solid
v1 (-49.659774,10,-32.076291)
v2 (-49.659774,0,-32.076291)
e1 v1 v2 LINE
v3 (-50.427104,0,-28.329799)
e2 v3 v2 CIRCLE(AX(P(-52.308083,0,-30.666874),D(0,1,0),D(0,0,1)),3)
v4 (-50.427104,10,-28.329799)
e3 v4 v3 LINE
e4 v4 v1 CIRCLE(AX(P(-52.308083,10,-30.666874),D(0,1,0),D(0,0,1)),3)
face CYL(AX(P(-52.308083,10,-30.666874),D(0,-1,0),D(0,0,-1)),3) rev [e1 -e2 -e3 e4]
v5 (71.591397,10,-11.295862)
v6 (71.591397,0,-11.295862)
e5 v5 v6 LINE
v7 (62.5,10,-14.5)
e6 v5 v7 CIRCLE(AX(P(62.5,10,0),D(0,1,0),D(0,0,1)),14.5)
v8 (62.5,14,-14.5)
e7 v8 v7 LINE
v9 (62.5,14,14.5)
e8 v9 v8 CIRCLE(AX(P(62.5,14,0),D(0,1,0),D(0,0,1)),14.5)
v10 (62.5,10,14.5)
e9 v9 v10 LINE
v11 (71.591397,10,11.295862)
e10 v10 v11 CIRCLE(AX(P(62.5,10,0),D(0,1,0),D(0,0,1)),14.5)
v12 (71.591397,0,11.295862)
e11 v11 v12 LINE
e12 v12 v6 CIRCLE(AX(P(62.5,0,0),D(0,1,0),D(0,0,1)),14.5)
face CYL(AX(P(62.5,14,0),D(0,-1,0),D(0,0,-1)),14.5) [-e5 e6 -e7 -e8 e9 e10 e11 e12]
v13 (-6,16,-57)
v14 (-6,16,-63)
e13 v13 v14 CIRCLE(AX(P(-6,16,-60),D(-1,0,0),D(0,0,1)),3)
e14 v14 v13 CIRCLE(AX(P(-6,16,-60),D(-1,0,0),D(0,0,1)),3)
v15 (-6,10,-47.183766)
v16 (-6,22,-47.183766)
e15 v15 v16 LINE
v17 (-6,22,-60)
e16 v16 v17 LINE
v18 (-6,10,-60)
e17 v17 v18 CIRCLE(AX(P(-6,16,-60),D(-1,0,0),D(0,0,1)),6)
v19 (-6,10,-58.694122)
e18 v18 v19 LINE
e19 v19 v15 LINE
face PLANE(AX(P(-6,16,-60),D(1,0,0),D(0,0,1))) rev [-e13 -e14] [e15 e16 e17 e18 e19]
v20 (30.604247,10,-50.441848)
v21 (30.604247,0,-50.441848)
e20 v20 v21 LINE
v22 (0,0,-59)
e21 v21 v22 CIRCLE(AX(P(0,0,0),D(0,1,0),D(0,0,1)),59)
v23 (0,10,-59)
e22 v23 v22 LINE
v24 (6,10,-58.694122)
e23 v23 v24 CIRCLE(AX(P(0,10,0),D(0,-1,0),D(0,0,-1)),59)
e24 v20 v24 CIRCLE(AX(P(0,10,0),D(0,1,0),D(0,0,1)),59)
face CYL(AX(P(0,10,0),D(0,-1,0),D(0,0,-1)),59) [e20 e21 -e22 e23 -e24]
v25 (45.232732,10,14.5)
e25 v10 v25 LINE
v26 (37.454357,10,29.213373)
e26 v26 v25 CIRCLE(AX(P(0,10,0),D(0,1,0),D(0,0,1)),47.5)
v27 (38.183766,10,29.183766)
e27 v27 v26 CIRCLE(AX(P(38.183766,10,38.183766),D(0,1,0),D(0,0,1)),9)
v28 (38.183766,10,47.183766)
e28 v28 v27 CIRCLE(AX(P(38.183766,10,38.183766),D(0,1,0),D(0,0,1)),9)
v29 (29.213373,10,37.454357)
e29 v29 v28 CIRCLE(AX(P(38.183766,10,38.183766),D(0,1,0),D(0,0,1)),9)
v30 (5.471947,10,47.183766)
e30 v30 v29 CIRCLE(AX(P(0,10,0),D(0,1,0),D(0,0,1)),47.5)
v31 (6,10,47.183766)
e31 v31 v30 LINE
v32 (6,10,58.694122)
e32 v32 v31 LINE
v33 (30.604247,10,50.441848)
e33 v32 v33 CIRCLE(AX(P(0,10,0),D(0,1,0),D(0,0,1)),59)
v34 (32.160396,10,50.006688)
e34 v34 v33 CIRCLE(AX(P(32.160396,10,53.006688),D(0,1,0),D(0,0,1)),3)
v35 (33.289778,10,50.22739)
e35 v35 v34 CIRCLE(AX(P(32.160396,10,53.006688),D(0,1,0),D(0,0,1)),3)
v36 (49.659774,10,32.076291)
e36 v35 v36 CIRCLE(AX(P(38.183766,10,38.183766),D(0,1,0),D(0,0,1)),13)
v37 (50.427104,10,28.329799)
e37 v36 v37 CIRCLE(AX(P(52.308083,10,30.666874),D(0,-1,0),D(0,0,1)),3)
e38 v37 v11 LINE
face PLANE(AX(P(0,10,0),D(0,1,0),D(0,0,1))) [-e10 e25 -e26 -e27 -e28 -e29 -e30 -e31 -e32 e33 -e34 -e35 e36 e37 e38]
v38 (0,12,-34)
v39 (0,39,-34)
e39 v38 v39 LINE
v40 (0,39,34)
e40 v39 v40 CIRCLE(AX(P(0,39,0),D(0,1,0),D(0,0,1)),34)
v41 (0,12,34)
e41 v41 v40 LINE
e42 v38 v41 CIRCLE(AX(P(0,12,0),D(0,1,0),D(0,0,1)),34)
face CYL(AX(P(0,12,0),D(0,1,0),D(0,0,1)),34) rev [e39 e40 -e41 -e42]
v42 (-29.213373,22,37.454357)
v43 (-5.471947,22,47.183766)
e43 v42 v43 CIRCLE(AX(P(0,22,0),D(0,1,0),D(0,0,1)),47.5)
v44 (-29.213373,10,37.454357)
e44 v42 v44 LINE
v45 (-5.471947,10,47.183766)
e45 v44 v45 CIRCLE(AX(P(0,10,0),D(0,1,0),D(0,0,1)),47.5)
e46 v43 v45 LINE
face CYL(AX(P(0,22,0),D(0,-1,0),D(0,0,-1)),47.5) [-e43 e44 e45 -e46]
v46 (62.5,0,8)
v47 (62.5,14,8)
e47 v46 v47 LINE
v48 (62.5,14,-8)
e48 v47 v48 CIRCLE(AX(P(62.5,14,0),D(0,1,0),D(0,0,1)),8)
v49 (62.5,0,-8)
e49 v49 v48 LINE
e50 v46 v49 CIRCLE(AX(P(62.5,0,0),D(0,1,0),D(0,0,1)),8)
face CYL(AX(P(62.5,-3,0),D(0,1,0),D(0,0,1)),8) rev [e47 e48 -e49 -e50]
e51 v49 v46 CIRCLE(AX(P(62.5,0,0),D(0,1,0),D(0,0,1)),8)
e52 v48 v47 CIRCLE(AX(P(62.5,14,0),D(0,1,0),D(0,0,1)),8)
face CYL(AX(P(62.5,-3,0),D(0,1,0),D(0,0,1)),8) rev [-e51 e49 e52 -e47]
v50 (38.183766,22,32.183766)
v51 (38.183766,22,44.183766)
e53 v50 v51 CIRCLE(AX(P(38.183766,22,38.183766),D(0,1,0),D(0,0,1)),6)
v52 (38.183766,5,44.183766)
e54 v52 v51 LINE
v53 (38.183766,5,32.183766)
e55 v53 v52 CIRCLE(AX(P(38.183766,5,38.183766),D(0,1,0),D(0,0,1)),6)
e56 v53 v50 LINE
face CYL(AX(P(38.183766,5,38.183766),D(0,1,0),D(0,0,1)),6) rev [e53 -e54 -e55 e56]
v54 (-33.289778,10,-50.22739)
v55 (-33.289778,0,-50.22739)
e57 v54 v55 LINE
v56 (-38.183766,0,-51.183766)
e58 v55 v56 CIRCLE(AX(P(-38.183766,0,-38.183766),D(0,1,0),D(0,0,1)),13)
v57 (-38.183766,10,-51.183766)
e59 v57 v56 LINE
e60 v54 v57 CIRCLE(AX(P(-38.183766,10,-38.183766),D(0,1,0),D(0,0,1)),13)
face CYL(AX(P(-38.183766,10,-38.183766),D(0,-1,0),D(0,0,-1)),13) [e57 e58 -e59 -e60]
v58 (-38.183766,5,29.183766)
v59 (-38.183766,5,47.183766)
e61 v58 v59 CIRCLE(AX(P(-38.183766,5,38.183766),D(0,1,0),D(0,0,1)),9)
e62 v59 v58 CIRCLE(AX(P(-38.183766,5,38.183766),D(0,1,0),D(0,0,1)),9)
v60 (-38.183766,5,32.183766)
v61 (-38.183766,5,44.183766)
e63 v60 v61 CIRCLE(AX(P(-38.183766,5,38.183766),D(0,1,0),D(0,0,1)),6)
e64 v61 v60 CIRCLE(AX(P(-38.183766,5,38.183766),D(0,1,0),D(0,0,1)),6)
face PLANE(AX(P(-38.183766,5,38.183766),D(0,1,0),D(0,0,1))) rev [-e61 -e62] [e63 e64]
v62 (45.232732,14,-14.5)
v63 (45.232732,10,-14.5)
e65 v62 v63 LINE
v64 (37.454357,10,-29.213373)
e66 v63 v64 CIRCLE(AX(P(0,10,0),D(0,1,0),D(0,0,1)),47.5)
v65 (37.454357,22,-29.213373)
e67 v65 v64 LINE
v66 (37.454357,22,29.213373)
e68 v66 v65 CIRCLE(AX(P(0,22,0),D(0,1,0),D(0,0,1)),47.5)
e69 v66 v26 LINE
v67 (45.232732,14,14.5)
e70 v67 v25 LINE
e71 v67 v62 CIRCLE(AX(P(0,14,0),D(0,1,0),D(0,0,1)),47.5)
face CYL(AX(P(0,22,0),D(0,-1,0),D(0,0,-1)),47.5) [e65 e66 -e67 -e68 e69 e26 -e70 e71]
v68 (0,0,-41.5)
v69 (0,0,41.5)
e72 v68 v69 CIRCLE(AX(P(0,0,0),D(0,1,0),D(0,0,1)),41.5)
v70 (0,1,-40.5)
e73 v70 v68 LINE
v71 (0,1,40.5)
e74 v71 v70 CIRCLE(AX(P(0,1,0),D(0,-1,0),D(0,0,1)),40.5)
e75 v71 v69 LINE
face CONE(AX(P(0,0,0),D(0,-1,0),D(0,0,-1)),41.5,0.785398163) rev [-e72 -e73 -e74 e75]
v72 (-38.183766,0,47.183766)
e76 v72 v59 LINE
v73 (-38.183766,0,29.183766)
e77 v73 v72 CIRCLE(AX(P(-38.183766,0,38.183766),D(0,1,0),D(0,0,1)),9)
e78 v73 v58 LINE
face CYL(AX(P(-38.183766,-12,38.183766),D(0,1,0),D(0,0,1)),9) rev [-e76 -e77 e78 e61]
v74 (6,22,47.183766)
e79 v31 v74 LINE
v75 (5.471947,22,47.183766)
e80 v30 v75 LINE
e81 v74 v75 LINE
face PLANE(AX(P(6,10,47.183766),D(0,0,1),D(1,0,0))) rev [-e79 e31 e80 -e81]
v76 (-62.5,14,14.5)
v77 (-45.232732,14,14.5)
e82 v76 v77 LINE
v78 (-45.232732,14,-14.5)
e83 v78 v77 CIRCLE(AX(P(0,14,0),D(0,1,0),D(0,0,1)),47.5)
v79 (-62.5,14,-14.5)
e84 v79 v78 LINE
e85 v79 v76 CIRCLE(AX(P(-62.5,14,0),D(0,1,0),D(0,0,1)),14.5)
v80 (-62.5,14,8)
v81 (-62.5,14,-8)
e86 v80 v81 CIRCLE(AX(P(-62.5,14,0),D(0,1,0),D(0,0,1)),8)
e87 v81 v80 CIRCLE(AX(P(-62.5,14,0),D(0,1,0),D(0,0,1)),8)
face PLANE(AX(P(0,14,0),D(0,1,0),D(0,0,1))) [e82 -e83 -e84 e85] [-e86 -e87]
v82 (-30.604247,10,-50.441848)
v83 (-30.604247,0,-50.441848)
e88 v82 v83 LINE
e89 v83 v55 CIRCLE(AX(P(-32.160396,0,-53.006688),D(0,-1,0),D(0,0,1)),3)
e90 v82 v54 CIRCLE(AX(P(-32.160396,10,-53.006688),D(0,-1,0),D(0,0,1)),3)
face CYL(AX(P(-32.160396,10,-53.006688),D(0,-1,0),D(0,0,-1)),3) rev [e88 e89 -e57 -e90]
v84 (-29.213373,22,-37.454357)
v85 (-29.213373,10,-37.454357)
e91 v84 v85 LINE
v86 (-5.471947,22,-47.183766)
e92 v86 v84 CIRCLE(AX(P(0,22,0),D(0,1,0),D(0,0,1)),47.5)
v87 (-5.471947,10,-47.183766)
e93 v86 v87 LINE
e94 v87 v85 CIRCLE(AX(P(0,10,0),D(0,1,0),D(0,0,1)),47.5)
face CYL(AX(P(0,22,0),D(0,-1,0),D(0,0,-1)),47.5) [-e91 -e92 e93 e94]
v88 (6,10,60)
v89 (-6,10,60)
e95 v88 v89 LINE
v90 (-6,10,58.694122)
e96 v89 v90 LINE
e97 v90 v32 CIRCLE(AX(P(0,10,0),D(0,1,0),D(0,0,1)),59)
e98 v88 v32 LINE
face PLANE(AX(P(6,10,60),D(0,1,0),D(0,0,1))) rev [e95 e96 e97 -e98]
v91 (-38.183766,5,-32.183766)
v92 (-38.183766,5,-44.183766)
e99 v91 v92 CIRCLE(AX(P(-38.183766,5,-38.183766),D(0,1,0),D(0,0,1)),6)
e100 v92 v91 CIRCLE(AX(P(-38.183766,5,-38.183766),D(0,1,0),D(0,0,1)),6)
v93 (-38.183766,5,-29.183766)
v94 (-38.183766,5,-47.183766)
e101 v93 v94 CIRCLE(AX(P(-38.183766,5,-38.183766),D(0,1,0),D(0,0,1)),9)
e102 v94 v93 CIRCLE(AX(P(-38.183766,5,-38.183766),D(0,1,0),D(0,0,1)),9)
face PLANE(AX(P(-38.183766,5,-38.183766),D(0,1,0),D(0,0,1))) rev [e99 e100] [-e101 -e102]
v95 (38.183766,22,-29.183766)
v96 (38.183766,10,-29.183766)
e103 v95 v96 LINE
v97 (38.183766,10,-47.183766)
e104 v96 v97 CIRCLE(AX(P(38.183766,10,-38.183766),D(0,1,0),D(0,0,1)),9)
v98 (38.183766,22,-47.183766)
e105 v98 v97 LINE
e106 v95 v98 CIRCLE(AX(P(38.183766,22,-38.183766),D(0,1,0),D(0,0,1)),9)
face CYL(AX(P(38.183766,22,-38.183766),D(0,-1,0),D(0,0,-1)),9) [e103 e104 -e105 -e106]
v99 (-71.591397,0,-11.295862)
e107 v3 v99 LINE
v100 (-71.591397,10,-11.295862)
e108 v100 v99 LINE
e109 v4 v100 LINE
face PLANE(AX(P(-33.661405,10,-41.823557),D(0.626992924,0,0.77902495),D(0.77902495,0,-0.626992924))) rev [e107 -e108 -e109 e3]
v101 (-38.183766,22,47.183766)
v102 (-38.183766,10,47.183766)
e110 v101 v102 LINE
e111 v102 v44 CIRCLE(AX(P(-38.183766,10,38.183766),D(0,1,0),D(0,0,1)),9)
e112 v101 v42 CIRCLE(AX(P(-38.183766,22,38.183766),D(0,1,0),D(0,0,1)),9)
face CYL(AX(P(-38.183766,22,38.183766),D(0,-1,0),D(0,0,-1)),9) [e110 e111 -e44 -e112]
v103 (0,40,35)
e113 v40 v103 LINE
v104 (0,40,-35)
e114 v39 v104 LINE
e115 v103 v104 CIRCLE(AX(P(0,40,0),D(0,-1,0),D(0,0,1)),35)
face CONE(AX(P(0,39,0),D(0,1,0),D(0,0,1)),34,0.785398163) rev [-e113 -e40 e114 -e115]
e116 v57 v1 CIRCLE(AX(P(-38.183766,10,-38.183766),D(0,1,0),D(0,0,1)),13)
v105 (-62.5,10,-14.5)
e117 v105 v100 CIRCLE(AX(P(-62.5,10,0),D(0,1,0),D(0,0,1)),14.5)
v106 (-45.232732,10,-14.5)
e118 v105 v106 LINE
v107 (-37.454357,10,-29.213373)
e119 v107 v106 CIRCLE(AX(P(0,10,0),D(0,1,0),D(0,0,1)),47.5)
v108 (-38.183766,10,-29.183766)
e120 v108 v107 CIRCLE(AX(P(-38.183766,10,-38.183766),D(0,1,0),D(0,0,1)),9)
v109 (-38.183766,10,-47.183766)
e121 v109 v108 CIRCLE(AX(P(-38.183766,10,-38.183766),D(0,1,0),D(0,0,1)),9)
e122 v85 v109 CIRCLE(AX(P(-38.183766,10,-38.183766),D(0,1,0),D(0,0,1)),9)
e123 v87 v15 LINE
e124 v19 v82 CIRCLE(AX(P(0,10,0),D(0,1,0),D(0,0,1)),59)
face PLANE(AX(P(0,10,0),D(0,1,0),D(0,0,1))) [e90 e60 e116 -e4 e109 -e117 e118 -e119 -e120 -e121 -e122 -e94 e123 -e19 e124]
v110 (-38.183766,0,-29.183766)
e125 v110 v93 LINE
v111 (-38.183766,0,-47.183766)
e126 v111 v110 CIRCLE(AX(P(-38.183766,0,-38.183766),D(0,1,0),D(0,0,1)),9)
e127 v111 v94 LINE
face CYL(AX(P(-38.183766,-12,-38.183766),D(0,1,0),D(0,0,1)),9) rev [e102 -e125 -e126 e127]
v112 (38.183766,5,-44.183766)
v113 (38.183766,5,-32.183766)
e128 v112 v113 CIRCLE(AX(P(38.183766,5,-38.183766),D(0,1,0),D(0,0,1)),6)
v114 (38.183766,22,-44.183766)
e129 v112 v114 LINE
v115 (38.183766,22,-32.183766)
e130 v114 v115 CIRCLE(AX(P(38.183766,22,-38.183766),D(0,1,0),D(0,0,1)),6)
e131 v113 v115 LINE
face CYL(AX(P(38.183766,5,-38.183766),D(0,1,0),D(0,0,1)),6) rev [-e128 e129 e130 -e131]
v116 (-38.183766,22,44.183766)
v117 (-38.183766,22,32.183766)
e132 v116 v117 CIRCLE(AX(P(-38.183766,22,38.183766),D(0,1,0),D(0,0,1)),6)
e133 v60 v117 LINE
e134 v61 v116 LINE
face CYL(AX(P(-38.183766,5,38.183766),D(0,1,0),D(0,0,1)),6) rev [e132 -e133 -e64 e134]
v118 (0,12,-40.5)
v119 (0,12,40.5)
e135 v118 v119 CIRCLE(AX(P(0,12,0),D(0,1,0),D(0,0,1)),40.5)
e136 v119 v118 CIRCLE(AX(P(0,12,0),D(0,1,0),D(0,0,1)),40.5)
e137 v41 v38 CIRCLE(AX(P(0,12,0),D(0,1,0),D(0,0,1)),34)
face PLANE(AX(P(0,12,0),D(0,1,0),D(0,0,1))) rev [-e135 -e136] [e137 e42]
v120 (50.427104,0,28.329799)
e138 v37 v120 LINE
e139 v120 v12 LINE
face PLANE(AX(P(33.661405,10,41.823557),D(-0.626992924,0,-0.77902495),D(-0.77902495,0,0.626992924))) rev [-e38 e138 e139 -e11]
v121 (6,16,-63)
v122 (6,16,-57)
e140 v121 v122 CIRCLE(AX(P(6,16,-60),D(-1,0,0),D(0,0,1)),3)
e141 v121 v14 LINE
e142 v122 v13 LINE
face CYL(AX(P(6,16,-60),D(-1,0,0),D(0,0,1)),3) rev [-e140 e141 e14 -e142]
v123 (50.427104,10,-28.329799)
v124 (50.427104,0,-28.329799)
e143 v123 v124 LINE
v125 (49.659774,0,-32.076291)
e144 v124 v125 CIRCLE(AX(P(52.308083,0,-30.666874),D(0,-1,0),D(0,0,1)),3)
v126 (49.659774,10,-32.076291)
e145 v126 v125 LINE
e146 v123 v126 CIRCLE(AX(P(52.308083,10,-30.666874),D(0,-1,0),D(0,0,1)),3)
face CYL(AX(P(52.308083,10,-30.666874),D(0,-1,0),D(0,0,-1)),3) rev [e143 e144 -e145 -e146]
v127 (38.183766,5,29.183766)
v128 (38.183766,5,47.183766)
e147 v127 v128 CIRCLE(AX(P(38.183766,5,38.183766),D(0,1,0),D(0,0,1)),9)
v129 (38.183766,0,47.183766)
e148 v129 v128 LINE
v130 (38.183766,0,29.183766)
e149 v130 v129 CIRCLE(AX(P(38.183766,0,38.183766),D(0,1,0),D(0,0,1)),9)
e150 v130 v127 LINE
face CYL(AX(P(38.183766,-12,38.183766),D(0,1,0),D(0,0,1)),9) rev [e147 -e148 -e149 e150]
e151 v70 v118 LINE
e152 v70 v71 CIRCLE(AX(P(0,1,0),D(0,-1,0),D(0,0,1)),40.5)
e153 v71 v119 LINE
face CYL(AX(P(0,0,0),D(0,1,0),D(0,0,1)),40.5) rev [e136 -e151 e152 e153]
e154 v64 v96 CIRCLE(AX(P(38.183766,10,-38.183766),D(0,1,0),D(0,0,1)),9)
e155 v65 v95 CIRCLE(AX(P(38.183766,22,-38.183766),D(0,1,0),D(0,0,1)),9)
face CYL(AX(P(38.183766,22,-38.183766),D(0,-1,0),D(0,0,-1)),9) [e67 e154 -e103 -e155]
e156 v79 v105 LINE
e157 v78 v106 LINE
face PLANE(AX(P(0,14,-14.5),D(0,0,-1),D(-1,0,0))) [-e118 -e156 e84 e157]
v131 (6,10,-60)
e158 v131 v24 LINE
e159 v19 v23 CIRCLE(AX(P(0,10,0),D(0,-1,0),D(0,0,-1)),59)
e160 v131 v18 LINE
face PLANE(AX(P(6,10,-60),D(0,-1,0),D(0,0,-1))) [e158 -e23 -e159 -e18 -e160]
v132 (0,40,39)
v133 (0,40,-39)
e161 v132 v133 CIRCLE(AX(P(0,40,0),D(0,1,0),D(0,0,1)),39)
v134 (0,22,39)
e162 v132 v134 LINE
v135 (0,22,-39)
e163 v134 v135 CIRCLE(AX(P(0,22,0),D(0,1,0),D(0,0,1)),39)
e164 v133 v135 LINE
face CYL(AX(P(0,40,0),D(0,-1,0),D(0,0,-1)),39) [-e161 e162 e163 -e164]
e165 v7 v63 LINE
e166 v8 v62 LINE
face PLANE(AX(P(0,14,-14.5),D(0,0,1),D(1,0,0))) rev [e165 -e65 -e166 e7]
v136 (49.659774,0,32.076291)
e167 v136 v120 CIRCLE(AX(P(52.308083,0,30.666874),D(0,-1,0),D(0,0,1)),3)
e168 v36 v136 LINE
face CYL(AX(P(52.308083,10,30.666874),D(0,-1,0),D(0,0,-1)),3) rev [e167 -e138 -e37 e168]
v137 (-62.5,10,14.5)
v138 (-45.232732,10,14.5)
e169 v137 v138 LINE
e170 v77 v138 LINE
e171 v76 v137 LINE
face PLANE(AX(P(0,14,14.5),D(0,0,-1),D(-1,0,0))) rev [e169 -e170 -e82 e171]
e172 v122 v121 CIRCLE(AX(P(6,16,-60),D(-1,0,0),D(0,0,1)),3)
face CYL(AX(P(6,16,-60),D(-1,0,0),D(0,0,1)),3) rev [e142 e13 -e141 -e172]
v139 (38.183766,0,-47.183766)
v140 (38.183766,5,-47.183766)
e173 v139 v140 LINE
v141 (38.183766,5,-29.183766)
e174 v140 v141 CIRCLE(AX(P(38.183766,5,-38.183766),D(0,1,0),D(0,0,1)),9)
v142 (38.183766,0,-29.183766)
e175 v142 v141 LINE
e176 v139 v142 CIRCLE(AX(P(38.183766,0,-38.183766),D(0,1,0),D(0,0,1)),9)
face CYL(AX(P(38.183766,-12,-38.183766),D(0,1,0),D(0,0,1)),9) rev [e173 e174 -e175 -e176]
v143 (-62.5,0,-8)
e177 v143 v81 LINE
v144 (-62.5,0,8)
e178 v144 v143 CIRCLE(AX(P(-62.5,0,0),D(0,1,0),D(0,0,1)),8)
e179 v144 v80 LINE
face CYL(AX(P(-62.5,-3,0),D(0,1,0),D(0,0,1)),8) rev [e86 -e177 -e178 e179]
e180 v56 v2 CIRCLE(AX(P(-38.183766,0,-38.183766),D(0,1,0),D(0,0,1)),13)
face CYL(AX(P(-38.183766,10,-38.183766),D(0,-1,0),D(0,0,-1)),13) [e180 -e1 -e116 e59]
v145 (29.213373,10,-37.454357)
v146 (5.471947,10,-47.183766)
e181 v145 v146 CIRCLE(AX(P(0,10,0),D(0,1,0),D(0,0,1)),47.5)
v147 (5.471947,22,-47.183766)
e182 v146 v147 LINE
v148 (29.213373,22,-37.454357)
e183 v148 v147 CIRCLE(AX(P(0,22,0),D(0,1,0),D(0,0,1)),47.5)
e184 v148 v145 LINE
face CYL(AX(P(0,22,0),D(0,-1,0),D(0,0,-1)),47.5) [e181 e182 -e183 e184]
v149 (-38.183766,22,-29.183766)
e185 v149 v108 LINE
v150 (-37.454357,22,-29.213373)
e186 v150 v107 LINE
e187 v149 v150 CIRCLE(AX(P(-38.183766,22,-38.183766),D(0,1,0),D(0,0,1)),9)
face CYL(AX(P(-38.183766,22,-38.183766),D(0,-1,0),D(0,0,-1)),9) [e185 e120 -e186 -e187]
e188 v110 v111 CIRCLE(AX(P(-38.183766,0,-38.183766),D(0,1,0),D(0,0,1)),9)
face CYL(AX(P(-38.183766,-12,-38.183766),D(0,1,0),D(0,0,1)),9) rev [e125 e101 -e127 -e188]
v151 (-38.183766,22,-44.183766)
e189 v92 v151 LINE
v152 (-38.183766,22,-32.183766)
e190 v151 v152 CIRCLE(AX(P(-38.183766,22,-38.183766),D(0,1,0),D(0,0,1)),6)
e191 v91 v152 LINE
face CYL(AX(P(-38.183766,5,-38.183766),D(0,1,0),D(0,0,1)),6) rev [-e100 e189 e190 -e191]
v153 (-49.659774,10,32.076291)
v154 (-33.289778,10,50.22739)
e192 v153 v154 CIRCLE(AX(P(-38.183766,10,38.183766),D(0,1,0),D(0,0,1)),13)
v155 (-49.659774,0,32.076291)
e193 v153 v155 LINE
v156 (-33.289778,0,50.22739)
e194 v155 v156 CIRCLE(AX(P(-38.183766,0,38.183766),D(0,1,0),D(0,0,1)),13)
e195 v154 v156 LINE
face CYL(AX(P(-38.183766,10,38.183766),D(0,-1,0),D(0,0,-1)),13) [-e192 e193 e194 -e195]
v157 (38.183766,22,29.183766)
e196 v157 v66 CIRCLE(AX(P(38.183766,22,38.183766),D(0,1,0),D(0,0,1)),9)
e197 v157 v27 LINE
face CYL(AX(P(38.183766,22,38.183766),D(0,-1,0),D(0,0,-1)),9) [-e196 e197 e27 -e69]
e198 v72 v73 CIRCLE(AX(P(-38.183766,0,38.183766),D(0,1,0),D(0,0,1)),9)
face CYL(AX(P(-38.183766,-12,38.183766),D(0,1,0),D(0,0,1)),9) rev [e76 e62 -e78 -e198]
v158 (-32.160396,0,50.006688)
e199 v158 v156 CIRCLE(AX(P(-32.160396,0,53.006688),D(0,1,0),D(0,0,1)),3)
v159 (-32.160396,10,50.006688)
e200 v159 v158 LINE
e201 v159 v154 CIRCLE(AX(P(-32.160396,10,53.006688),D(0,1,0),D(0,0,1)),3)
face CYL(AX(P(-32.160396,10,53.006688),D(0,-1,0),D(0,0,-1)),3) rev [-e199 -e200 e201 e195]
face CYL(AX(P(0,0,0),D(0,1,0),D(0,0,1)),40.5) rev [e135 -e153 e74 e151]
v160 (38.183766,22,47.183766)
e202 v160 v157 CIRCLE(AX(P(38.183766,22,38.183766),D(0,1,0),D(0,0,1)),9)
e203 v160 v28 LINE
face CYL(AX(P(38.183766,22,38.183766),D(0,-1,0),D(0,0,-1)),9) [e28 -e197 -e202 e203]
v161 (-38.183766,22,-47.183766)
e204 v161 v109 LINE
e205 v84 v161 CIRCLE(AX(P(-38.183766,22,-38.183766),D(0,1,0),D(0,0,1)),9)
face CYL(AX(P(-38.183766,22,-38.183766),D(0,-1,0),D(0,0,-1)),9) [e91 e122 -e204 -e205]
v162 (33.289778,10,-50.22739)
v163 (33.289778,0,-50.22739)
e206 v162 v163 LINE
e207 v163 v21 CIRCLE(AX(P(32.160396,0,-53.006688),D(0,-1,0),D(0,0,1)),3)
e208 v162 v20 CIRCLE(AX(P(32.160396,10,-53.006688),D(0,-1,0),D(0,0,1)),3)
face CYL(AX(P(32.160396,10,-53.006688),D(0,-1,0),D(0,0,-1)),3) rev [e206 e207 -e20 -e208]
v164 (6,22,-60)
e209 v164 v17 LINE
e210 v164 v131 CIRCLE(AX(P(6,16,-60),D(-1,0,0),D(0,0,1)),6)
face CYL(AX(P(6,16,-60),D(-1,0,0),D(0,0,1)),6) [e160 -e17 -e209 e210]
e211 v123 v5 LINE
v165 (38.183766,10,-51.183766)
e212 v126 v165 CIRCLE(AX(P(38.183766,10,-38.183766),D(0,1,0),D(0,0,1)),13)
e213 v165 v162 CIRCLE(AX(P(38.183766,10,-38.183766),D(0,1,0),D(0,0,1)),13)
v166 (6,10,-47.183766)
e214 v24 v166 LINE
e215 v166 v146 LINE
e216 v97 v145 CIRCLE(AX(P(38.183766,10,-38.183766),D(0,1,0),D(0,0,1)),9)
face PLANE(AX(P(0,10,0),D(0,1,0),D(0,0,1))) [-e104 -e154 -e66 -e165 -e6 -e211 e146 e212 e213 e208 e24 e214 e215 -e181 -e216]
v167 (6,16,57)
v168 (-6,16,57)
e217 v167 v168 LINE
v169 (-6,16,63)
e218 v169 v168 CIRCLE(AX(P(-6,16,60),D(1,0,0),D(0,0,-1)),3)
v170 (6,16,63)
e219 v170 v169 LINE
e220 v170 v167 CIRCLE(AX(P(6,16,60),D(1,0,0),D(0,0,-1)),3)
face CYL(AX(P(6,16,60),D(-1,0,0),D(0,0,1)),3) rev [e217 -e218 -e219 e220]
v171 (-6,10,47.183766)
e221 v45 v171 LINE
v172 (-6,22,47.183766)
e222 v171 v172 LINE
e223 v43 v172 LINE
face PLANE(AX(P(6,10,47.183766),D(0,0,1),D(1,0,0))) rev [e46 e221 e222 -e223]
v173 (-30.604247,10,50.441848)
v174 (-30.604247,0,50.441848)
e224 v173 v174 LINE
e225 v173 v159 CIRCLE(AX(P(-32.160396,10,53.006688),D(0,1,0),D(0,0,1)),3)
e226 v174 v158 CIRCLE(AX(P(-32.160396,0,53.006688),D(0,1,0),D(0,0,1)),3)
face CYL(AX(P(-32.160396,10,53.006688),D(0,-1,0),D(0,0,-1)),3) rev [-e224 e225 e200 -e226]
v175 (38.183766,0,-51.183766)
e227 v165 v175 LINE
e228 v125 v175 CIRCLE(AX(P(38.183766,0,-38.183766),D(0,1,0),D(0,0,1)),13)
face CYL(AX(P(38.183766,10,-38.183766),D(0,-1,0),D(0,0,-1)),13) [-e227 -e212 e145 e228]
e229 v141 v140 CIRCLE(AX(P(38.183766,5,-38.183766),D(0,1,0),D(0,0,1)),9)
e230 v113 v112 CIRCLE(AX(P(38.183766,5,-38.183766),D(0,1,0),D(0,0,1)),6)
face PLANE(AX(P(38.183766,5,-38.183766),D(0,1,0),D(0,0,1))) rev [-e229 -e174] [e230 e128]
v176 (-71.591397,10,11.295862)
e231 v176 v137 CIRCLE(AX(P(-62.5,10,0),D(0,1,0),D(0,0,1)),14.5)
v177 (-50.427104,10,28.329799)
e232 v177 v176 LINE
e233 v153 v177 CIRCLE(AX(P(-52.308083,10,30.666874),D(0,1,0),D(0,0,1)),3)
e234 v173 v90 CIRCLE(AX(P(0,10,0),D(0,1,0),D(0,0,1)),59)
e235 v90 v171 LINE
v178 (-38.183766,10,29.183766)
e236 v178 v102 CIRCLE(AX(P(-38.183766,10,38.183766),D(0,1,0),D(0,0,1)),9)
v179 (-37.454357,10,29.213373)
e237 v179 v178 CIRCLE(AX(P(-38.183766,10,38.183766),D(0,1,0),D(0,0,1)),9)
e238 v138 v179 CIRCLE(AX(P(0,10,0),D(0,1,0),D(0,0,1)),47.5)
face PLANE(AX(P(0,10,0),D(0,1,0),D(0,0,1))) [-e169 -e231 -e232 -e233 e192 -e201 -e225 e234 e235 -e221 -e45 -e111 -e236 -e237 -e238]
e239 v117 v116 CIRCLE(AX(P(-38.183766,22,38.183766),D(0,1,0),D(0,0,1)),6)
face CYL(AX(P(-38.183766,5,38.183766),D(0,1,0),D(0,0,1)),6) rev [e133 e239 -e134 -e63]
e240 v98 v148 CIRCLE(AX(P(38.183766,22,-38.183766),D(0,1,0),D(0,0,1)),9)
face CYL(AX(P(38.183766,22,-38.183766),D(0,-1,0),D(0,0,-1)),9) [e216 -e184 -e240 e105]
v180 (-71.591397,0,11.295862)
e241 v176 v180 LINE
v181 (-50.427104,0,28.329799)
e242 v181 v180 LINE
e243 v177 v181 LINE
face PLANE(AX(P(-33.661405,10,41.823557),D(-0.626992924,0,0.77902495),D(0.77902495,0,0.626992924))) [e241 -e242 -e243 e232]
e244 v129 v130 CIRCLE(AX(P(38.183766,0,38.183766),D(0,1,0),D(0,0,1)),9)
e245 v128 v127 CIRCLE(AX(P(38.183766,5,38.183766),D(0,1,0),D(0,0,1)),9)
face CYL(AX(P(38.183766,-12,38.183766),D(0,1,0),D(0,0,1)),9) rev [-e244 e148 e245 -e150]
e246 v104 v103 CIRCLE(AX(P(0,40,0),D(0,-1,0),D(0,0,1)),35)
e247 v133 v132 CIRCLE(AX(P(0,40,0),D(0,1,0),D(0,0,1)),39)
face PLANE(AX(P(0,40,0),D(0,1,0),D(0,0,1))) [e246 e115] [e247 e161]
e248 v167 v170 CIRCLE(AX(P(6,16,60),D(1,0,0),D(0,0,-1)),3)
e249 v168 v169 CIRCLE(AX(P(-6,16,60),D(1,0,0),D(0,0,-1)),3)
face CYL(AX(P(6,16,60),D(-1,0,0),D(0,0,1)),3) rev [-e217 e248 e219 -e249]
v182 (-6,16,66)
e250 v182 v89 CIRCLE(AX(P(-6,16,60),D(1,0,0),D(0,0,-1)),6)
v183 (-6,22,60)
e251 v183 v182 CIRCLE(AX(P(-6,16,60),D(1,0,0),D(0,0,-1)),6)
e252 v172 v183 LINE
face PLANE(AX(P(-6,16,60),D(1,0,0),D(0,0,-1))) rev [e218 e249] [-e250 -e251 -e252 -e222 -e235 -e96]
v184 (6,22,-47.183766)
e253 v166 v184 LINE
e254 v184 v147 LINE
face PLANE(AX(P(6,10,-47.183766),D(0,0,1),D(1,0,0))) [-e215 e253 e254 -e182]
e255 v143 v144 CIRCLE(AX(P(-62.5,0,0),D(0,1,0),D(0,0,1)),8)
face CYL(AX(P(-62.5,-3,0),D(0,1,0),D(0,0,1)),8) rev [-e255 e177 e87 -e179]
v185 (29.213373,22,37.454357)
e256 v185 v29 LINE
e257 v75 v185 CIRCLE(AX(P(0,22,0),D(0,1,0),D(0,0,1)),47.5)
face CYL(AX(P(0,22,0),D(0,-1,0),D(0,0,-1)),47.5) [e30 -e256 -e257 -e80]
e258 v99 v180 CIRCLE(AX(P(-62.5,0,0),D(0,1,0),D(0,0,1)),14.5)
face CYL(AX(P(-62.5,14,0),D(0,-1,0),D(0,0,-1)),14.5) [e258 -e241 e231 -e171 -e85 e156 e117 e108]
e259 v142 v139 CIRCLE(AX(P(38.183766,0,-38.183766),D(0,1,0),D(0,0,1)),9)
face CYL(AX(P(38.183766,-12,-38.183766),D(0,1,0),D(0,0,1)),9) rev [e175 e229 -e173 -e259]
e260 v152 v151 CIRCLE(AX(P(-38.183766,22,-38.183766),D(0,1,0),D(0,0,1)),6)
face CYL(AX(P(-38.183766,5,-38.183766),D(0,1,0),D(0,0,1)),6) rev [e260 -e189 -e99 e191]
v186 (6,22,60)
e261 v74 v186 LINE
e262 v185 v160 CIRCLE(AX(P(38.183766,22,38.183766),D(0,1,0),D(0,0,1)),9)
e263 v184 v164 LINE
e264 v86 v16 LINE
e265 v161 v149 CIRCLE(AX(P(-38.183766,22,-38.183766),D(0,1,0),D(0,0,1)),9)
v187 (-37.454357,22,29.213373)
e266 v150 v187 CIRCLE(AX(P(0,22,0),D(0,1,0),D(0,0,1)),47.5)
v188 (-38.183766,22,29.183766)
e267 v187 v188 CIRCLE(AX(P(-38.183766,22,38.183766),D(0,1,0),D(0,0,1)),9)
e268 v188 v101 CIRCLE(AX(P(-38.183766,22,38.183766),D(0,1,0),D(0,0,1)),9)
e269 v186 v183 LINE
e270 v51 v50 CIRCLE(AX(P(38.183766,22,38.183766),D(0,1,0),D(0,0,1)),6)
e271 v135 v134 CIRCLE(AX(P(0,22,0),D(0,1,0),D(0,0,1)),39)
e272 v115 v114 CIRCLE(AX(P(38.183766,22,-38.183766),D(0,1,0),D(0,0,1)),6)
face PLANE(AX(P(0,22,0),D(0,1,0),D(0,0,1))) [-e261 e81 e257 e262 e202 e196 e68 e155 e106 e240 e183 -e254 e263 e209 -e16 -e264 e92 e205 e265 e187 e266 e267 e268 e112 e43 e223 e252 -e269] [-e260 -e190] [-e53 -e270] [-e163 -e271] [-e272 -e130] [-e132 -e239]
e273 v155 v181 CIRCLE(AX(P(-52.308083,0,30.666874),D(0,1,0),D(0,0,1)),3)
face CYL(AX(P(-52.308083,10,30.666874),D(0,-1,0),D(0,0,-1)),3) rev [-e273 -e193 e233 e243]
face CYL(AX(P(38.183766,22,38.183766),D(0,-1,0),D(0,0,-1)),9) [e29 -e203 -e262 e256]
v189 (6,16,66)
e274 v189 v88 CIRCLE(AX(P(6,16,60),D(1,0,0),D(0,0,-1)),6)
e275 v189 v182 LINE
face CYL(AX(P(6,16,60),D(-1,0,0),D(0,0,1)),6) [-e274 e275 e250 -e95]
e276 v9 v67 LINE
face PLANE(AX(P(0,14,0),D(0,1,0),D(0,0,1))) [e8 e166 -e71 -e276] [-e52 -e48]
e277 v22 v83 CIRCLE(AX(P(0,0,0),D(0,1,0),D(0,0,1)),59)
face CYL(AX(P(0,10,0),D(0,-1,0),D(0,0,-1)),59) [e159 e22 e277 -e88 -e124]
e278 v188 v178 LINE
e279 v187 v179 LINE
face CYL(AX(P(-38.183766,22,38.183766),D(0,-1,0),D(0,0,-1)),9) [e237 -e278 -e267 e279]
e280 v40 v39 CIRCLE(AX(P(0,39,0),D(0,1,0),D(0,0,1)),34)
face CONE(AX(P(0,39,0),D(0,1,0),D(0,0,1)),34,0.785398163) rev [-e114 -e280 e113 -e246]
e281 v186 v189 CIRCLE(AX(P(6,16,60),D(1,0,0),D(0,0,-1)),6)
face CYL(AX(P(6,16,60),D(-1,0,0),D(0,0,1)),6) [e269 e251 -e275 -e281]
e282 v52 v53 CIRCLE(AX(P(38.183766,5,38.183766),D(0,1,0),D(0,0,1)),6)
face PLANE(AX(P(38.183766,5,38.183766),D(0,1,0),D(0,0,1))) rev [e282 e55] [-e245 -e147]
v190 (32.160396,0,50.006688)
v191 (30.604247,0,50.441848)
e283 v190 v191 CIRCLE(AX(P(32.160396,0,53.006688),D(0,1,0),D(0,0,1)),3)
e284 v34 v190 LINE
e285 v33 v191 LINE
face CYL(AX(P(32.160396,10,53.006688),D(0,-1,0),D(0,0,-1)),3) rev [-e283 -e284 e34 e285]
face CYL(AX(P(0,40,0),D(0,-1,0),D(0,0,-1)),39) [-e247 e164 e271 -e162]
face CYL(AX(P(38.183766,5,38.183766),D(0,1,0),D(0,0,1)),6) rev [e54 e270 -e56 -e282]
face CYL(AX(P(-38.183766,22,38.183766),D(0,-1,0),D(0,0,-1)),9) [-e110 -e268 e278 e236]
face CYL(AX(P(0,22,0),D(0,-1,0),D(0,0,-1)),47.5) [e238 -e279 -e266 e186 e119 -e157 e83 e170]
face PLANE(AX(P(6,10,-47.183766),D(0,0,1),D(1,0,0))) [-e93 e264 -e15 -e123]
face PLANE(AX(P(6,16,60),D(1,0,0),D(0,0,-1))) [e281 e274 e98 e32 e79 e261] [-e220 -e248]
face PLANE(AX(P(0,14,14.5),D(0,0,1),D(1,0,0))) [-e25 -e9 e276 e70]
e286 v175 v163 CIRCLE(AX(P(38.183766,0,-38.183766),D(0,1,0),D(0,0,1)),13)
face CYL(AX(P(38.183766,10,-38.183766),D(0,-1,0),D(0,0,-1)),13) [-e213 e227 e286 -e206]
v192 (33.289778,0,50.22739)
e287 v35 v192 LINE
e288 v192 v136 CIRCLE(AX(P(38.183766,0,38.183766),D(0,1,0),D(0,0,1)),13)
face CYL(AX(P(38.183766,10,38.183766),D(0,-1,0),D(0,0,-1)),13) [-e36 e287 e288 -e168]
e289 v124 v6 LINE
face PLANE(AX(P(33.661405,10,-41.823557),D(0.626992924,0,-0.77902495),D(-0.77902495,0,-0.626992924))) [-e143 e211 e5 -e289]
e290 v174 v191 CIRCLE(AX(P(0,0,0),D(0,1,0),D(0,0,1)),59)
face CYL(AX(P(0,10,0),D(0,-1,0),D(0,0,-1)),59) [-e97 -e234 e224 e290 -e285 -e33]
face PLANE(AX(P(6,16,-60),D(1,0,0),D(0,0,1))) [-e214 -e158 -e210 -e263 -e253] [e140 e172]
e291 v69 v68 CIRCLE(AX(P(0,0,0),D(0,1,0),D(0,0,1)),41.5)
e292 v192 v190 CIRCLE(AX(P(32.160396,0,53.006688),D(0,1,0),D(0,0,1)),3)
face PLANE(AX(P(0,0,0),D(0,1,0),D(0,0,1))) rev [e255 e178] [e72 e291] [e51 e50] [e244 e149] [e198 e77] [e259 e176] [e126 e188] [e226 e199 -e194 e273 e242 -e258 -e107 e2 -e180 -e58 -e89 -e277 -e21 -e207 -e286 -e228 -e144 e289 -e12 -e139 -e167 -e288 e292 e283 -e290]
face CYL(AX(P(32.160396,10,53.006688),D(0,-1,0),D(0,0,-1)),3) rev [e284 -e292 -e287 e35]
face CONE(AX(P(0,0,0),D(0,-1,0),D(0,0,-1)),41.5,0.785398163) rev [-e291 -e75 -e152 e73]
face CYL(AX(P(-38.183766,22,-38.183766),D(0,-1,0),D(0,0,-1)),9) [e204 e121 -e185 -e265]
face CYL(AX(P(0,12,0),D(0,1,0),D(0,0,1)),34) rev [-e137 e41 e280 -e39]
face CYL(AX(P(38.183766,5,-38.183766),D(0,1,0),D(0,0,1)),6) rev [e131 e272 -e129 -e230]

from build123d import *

# Parameters (mm, degrees)
BASE_FLANGE_DEPTH            = 10
MOUNTING_BOSSES_DEPTH        = 14
LUG_PADS_DEPTH               = 12
SIDE_EAR_SKETCH_R            = 3
SIDE_EAR_DEPTH               = 6
NECK_SKETCH_78_R             = 39
NECK_78_DEPTH                = 18
BORE_SKETCH_68_R             = 34
BORE_68_DEPTH                = 28
COUNTERBORE_SKETCH_81_R      = 40.5
COUNTERBORE_81_DEPTH         = 12
BORE_CHAMFER_1MM_SIZE        = 1
COUNTERBORE_CHAMFER_1MM_SIZE = 1
LUG_HOLES_SKETCH_R           = 6
LUG_HOLES_4X_12_DEPTH        = 17
LUG_START                    = -17
LUG_RELIEF_SKETCH_R          = 9
LUG_RELIEF_CUTS_DEPTH        = 17
BOSS_HOLES_SKETCH_R          = 8
BOSS_HOLES_16_DEPTH          = 17


with BuildPart() as part:
    # Base Flange Sketch → Base Flange (new body)
    with BuildSketch(Plane(origin=(0, 0, 0), x_dir=(1, 0, 0), z_dir=(0, 1, 0))):
        with BuildLine():
            Line((-45.232731512, -14.5), (-62.5, -14.5))
            ThreePointArc((-62.5, -14.5), (-67.319751251, -13.675525507), (-71.591397402, -11.295861777))
            Line((-71.591397402, -11.295861777), (-50.427104316, -28.329798892))
            ThreePointArc((-50.427104316, -28.329798892), (-49.36909282, -30.064930059), (-49.659773669, -32.076291075))
            ThreePointArc((-49.659773669, -32.076291075), (-47.837591407, -46.890295835), (-33.289777567, -50.227390033))
            ThreePointArc((-33.289777567, -50.227390033), (-31.921585171, -50.016208018), (-30.604247405, -50.44184811))
            ThreePointArc((-30.604247405, -50.44184811), (0, -59), (30.604247405, -50.44184811))
            ThreePointArc((30.604247405, -50.44184811), (31.921585171, -50.016208018), (33.289777567, -50.227390033))
            ThreePointArc((33.289777567, -50.227390033), (47.837591407, -46.890295835), (49.659773669, -32.076291075))
            ThreePointArc((49.659773669, -32.076291075), (49.36909282, -30.064930059), (50.427104316, -28.329798892))
            Line((50.427104316, -28.329798892), (71.591397402, -11.295861777))
            ThreePointArc((71.591397402, -11.295861777), (67.319751251, -13.675525507), (62.5, -14.5))
            Line((62.5, -14.5), (45.232731512, -14.5))
            ThreePointArc((45.232731512, -14.5), (43.022471721, -20.132484374), (40.114125183, -25.438297128))
            ThreePointArc((40.114125183, -25.438297128), (39.792711515, -27.966518872), (41.531678205, -29.829636361))
            ThreePointArc((41.531678205, -29.829636361), (44.547727215, -44.547727215), (29.829636361, -41.531678205))
            ThreePointArc((29.829636361, -41.531678205), (27.966518872, -39.792711515), (25.438297128, -40.114125183))
            ThreePointArc((25.438297128, -40.114125183), (0, -47.5), (-25.438297128, -40.114125183))
            ThreePointArc((-25.438297128, -40.114125183), (-27.966518872, -39.792711515), (-29.829636361, -41.531678205))
            ThreePointArc((-29.829636361, -41.531678205), (-44.547727215, -44.547727215), (-41.531678205, -29.829636361))
            ThreePointArc((-41.531678205, -29.829636361), (-39.792711515, -27.966518872), (-40.114125183, -25.438297128))
            ThreePointArc((-40.114125183, -25.438297128), (-43.022471721, -20.132484374), (-45.232731512, -14.5))
        make_face()
        with BuildLine():
            Line((-62.5, 14.5), (-45.232731512, 14.5))
            ThreePointArc((-45.232731512, 14.5), (-43.022471721, 20.132484374), (-40.114125183, 25.438297128))
            ThreePointArc((-40.114125183, 25.438297128), (-39.792711515, 27.966518872), (-41.531678205, 29.829636361))
            ThreePointArc((-41.531678205, 29.829636361), (-44.547727215, 44.547727215), (-29.829636361, 41.531678205))
            ThreePointArc((-29.829636361, 41.531678205), (-27.966518872, 39.792711515), (-25.438297128, 40.114125183))
            ThreePointArc((-25.438297128, 40.114125183), (0, 47.5), (25.438297128, 40.114125183))
            ThreePointArc((25.438297128, 40.114125183), (27.966518872, 39.792711515), (29.829636361, 41.531678205))
            ThreePointArc((29.829636361, 41.531678205), (44.547727215, 44.547727215), (41.531678205, 29.829636361))
            ThreePointArc((41.531678205, 29.829636361), (39.792711515, 27.966518872), (40.114125183, 25.438297128))
            ThreePointArc((40.114125183, 25.438297128), (43.022471721, 20.132484374), (45.232731512, 14.5))
            Line((45.232731512, 14.5), (62.5, 14.5))
            ThreePointArc((62.5, 14.5), (67.319751251, 13.675525507), (71.591397402, 11.295861777))
            Line((71.591397402, 11.295861777), (50.427104316, 28.329798892))
            ThreePointArc((50.427104316, 28.329798892), (49.36909282, 30.064930059), (49.659773669, 32.076291075))
            ThreePointArc((49.659773669, 32.076291075), (47.837591407, 46.890295835), (33.289777567, 50.227390033))
            ThreePointArc((33.289777567, 50.227390033), (31.921585171, 50.016208018), (30.604247405, 50.44184811))
            ThreePointArc((30.604247405, 50.44184811), (0, 59), (-30.604247405, 50.44184811))
            ThreePointArc((-30.604247405, 50.44184811), (-31.921585171, 50.016208018), (-33.289777567, 50.227390033))
            ThreePointArc((-33.289777567, 50.227390033), (-47.837591407, 46.890295835), (-49.659773669, 32.076291075))
            ThreePointArc((-49.659773669, 32.076291075), (-49.36909282, 30.064930059), (-50.427104316, 28.329798892))
            Line((-50.427104316, 28.329798892), (-71.591397402, 11.295861777))
            ThreePointArc((-71.591397402, 11.295861777), (-67.319751251, 13.675525507), (-62.5, 14.5))
        make_face()
        with BuildLine():
            ThreePointArc((-25.438297128, -40.114125183), (-27.966518872, -39.792711515), (-29.829636361, -41.531678205))
            ThreePointArc((-29.829636361, -41.531678205), (-44.547727215, -44.547727215), (-41.531678205, -29.829636361))
            ThreePointArc((-41.531678205, -29.829636361), (-39.792711515, -27.966518872), (-40.114125183, -25.438297128))
            ThreePointArc((-40.114125183, -25.438297128), (-47.5, 0), (-40.114125183, 25.438297128))
            ThreePointArc((-40.114125183, 25.438297128), (-39.792711515, 27.966518872), (-41.531678205, 29.829636361))
            ThreePointArc((-41.531678205, 29.829636361), (-44.547727215, 44.547727215), (-29.829636361, 41.531678205))
            ThreePointArc((-29.829636361, 41.531678205), (-27.966518872, 39.792711515), (-25.438297128, 40.114125183))
            ThreePointArc((-25.438297128, 40.114125183), (0, 47.5), (25.438297128, 40.114125183))
            ThreePointArc((25.438297128, 40.114125183), (27.966518872, 39.792711515), (29.829636361, 41.531678205))
            ThreePointArc((29.829636361, 41.531678205), (44.547727215, 44.547727215), (41.531678205, 29.829636361))
            ThreePointArc((41.531678205, 29.829636361), (39.792711515, 27.966518872), (40.114125183, 25.438297128))
            ThreePointArc((40.114125183, 25.438297128), (47.5, 0), (40.114125183, -25.438297128))
            ThreePointArc((40.114125183, -25.438297128), (39.792711515, -27.966518872), (41.531678205, -29.829636361))
            ThreePointArc((41.531678205, -29.829636361), (44.547727215, -44.547727215), (29.829636361, -41.531678205))
            ThreePointArc((29.829636361, -41.531678205), (27.966518872, -39.792711515), (25.438297128, -40.114125183))
            ThreePointArc((25.438297128, -40.114125183), (0, -47.5), (-25.438297128, -40.114125183))
        make_face()
    extrude(amount=BASE_FLANGE_DEPTH)

    # Sketch1_5 → Mounting Bosses (add)
    with BuildSketch(Plane(origin=(0, 0, 0), x_dir=(1, 0, 0), z_dir=(0, 1, 0))):
        with BuildLine():
            ThreePointArc((-71.591397402, -11.295861777), (-67.319751251, -13.675525507), (-62.5, -14.5))
            Line((-62.5, -14.5), (-45.232731512, -14.5))
            ThreePointArc((-45.232731512, -14.5), (-47.5, 0), (-45.232731512, 14.5))
            Line((-45.232731512, 14.5), (-62.5, 14.5))
            ThreePointArc((-62.5, 14.5), (-67.319751251, 13.675525507), (-71.591397402, 11.295861777))
            ThreePointArc((-71.591397402, 11.295861777), (-77, 0), (-71.591397402, -11.295861777))
        make_face()
        with BuildLine():
            ThreePointArc((45.232731512, 14.5), (47.5, 0), (45.232731512, -14.5))
            Line((45.232731512, -14.5), (62.5, -14.5))
            ThreePointArc((62.5, -14.5), (67.319751251, -13.675525507), (71.591397402, -11.295861777))
            ThreePointArc((71.591397402, -11.295861777), (77, 0), (71.591397402, 11.295861777))
            ThreePointArc((71.591397402, 11.295861777), (67.319751251, 13.675525507), (62.5, 14.5))
            Line((62.5, 14.5), (45.232731512, 14.5))
        make_face()
    extrude(amount=MOUNTING_BOSSES_DEPTH)

    # Lug Pads Sketch → Lug Pads (add)
    with BuildSketch(Plane(origin=(0, 10, 0), x_dir=(1, 0, 0), z_dir=(0, 1, 0))):
        with BuildLine():
            ThreePointArc((45.232731512, -14.5), (46.929759997, -7.338094208), (47.5, 0))
            ThreePointArc((47.5, 0), (46.929759997, 7.338094208), (45.232731512, 14.5))
            ThreePointArc((45.232731512, 14.5), (41.992969513, 22.200011521), (37.454357099, 29.213372526))
            ThreePointArc((37.454357099, 29.213372526), (33.587572106, 33.587572106), (29.213372526, 37.454357099))
            ThreePointArc((29.213372526, 37.454357099), (0, 47.5), (-29.213372526, 37.454357099))
            ThreePointArc((-29.213372526, 37.454357099), (-33.587572106, 33.587572106), (-37.454357099, 29.213372526))
            ThreePointArc((-37.454357099, 29.213372526), (-41.992969513, 22.200011521), (-45.232731512, 14.5))
            ThreePointArc((-45.232731512, 14.5), (-47.5, 0), (-45.232731512, -14.5))
            ThreePointArc((-45.232731512, -14.5), (-41.992969513, -22.200011521), (-37.454357099, -29.213372526))
            ThreePointArc((-37.454357099, -29.213372526), (-33.587572106, -33.587572106), (-29.213372526, -37.454357099))
            ThreePointArc((-29.213372526, -37.454357099), (0, -47.5), (29.213372526, -37.454357099))
            ThreePointArc((29.213372526, -37.454357099), (33.587572106, -33.587572106), (37.454357099, -29.213372526))
            ThreePointArc((37.454357099, -29.213372526), (41.992969513, -22.200011521), (45.232731512, -14.5))
        make_face()
        with BuildLine():
            ThreePointArc((-37.454357099, -29.213372526), (-44.547727215, -44.547727215), (-29.213372526, -37.454357099))
            ThreePointArc((-29.213372526, -37.454357099), (-33.587572106, -33.587572106), (-37.454357099, -29.213372526))
        make_face()
        with BuildLine():
            ThreePointArc((29.213372526, -37.454357099), (44.547727215, -44.547727215), (37.454357099, -29.213372526))
            ThreePointArc((37.454357099, -29.213372526), (33.587572106, -33.587572106), (29.213372526, -37.454357099))
        make_face()
        with BuildLine():
            ThreePointArc((29.213372526, 37.454357099), (33.587572106, 33.587572106), (37.454357099, 29.213372526))
            ThreePointArc((37.454357099, 29.213372526), (44.547727215, 44.547727215), (29.213372526, 37.454357099))
        make_face()
        with BuildLine():
            ThreePointArc((-37.454357099, 29.213372526), (-33.587572106, 33.587572106), (-29.213372526, 37.454357099))
            ThreePointArc((-29.213372526, 37.454357099), (-44.547727215, 44.547727215), (-37.454357099, 29.213372526))
        make_face()
    extrude(amount=LUG_PADS_DEPTH)

    # Side Ear Sketch → Side Ear (add, symmetric)
    with BuildSketch(Plane(origin=(0, 0, 0), x_dir=(0, 0, -1), z_dir=(1, 0, 0))):
        with BuildLine():
            Line((-60, 10), (-47.183766184, 10))
            Line((-47.183766184, 10), (-47.183766184, 22))
            Line((-47.183766184, 22), (-60, 22))
            ThreePointArc((-60, 22), (-66, 16), (-60, 10))
        make_face()
        with Locations((-60, 16)):
            Circle(SIDE_EAR_SKETCH_R, mode=Mode.SUBTRACT)
    side_ear = extrude(amount=SIDE_EAR_DEPTH, both=True)

    # Side Ear Mirror: Side Ear across plane
    add(side_ear.mirror(Plane.XY))

    # Neck Sketch _78 → Neck _78 (add)
    with BuildSketch(Plane(origin=(0, 22, 0), x_dir=(1, 0, 0), z_dir=(0, 1, 0))):
        with Locations(Location((0, 0, 0), (0, 0, 270))):
            Circle(NECK_SKETCH_78_R)
    extrude(amount=NECK_78_DEPTH)

    # Bore Sketch _68 → Bore _68 (cut)
    with BuildSketch(Plane(origin=(0, 40, 0), x_dir=(1, 0, 0), z_dir=(0, 1, 0))):
        with Locations(Location((0, 0, 0), (0, 0, 270))):
            Circle(BORE_SKETCH_68_R)
    extrude(amount=-BORE_68_DEPTH, mode=Mode.SUBTRACT)

    # Counterbore Sketch _81 → Counterbore _81 (cut)
    with BuildSketch(Plane(origin=(0, 12, 0), x_dir=(1, 0, 0), z_dir=(0, 1, 0))):
        with Locations(Location((0, 0, 0), (0, 0, 270))):
            Circle(COUNTERBORE_SKETCH_81_R)
    extrude(amount=-COUNTERBORE_81_DEPTH, mode=Mode.SUBTRACT)

    # Bore Chamfer 1mm
    bore_chamfer_1mm_edges = [part.edges().sort_by_distance(p)[0] for p in [
        (0, 40, -34),
    ]]
    chamfer(bore_chamfer_1mm_edges, length=BORE_CHAMFER_1MM_SIZE)

    # Counterbore Chamfer 1mm
    counterbore_chamfer_1mm_edges = [part.edges().sort_by_distance(p)[0] for p in [
        (0, 0, -40.5),
    ]]
    chamfer(counterbore_chamfer_1mm_edges, length=COUNTERBORE_CHAMFER_1MM_SIZE)

    # Lug Holes Sketch → Lug Holes 4x_12 (cut)
    with BuildSketch(Plane(origin=(0, 22, 0), x_dir=(1, 0, 0), z_dir=(0, 1, 0))):
        with Locations(Location((-38.183766184, 38.183766184, 0), (0, 0, 270))):
            Circle(LUG_HOLES_SKETCH_R)
        with Locations(Location((38.183766184, 38.183766184, 0), (0, 0, 270))):
            Circle(LUG_HOLES_SKETCH_R)
        with Locations(Location((38.183766184, -38.183766184, 0), (0, 0, 270))):
            Circle(LUG_HOLES_SKETCH_R)
        with Locations(Location((-38.183766184, -38.183766184, 0), (0, 0, 270))):
            Circle(LUG_HOLES_SKETCH_R)
    extrude(amount=-LUG_HOLES_4X_12_DEPTH, mode=Mode.SUBTRACT)

    # Lug Relief Sketch → Lug Relief Cuts (cut)
    with BuildSketch(Plane(origin=(0, 5, 0), x_dir=(1, 0, 0), z_dir=(0, 1, 0)).offset(LUG_START)):
        with Locations(Location((-38.183766184, 38.183766184, 0), (0, 0, 270))):
            Circle(LUG_RELIEF_SKETCH_R)
        with Locations(Location((38.183766184, 38.183766184, 0), (0, 0, 270))):
            Circle(LUG_RELIEF_SKETCH_R)
        with Locations(Location((38.183766184, -38.183766184, 0), (0, 0, 270))):
            Circle(LUG_RELIEF_SKETCH_R)
        with Locations(Location((-38.183766184, -38.183766184, 0), (0, 0, 270))):
            Circle(LUG_RELIEF_SKETCH_R)
    extrude(amount=LUG_RELIEF_CUTS_DEPTH, mode=Mode.SUBTRACT)

    # Boss Holes Sketch → Boss Holes _16 (cut)
    with BuildSketch(Plane(origin=(0, 14, 0), x_dir=(1, 0, 0), z_dir=(0, 1, 0))):
        with Locations(Location((-62.5, 0, 0), (0, 0, 270))):
            Circle(BOSS_HOLES_SKETCH_R)
        with Locations(Location((62.5, 0, 0), (0, 0, 270))):
            Circle(BOSS_HOLES_SKETCH_R)
    extrude(amount=-BOSS_HOLES_16_DEPTH, mode=Mode.SUBTRACT)


solid = part.part
